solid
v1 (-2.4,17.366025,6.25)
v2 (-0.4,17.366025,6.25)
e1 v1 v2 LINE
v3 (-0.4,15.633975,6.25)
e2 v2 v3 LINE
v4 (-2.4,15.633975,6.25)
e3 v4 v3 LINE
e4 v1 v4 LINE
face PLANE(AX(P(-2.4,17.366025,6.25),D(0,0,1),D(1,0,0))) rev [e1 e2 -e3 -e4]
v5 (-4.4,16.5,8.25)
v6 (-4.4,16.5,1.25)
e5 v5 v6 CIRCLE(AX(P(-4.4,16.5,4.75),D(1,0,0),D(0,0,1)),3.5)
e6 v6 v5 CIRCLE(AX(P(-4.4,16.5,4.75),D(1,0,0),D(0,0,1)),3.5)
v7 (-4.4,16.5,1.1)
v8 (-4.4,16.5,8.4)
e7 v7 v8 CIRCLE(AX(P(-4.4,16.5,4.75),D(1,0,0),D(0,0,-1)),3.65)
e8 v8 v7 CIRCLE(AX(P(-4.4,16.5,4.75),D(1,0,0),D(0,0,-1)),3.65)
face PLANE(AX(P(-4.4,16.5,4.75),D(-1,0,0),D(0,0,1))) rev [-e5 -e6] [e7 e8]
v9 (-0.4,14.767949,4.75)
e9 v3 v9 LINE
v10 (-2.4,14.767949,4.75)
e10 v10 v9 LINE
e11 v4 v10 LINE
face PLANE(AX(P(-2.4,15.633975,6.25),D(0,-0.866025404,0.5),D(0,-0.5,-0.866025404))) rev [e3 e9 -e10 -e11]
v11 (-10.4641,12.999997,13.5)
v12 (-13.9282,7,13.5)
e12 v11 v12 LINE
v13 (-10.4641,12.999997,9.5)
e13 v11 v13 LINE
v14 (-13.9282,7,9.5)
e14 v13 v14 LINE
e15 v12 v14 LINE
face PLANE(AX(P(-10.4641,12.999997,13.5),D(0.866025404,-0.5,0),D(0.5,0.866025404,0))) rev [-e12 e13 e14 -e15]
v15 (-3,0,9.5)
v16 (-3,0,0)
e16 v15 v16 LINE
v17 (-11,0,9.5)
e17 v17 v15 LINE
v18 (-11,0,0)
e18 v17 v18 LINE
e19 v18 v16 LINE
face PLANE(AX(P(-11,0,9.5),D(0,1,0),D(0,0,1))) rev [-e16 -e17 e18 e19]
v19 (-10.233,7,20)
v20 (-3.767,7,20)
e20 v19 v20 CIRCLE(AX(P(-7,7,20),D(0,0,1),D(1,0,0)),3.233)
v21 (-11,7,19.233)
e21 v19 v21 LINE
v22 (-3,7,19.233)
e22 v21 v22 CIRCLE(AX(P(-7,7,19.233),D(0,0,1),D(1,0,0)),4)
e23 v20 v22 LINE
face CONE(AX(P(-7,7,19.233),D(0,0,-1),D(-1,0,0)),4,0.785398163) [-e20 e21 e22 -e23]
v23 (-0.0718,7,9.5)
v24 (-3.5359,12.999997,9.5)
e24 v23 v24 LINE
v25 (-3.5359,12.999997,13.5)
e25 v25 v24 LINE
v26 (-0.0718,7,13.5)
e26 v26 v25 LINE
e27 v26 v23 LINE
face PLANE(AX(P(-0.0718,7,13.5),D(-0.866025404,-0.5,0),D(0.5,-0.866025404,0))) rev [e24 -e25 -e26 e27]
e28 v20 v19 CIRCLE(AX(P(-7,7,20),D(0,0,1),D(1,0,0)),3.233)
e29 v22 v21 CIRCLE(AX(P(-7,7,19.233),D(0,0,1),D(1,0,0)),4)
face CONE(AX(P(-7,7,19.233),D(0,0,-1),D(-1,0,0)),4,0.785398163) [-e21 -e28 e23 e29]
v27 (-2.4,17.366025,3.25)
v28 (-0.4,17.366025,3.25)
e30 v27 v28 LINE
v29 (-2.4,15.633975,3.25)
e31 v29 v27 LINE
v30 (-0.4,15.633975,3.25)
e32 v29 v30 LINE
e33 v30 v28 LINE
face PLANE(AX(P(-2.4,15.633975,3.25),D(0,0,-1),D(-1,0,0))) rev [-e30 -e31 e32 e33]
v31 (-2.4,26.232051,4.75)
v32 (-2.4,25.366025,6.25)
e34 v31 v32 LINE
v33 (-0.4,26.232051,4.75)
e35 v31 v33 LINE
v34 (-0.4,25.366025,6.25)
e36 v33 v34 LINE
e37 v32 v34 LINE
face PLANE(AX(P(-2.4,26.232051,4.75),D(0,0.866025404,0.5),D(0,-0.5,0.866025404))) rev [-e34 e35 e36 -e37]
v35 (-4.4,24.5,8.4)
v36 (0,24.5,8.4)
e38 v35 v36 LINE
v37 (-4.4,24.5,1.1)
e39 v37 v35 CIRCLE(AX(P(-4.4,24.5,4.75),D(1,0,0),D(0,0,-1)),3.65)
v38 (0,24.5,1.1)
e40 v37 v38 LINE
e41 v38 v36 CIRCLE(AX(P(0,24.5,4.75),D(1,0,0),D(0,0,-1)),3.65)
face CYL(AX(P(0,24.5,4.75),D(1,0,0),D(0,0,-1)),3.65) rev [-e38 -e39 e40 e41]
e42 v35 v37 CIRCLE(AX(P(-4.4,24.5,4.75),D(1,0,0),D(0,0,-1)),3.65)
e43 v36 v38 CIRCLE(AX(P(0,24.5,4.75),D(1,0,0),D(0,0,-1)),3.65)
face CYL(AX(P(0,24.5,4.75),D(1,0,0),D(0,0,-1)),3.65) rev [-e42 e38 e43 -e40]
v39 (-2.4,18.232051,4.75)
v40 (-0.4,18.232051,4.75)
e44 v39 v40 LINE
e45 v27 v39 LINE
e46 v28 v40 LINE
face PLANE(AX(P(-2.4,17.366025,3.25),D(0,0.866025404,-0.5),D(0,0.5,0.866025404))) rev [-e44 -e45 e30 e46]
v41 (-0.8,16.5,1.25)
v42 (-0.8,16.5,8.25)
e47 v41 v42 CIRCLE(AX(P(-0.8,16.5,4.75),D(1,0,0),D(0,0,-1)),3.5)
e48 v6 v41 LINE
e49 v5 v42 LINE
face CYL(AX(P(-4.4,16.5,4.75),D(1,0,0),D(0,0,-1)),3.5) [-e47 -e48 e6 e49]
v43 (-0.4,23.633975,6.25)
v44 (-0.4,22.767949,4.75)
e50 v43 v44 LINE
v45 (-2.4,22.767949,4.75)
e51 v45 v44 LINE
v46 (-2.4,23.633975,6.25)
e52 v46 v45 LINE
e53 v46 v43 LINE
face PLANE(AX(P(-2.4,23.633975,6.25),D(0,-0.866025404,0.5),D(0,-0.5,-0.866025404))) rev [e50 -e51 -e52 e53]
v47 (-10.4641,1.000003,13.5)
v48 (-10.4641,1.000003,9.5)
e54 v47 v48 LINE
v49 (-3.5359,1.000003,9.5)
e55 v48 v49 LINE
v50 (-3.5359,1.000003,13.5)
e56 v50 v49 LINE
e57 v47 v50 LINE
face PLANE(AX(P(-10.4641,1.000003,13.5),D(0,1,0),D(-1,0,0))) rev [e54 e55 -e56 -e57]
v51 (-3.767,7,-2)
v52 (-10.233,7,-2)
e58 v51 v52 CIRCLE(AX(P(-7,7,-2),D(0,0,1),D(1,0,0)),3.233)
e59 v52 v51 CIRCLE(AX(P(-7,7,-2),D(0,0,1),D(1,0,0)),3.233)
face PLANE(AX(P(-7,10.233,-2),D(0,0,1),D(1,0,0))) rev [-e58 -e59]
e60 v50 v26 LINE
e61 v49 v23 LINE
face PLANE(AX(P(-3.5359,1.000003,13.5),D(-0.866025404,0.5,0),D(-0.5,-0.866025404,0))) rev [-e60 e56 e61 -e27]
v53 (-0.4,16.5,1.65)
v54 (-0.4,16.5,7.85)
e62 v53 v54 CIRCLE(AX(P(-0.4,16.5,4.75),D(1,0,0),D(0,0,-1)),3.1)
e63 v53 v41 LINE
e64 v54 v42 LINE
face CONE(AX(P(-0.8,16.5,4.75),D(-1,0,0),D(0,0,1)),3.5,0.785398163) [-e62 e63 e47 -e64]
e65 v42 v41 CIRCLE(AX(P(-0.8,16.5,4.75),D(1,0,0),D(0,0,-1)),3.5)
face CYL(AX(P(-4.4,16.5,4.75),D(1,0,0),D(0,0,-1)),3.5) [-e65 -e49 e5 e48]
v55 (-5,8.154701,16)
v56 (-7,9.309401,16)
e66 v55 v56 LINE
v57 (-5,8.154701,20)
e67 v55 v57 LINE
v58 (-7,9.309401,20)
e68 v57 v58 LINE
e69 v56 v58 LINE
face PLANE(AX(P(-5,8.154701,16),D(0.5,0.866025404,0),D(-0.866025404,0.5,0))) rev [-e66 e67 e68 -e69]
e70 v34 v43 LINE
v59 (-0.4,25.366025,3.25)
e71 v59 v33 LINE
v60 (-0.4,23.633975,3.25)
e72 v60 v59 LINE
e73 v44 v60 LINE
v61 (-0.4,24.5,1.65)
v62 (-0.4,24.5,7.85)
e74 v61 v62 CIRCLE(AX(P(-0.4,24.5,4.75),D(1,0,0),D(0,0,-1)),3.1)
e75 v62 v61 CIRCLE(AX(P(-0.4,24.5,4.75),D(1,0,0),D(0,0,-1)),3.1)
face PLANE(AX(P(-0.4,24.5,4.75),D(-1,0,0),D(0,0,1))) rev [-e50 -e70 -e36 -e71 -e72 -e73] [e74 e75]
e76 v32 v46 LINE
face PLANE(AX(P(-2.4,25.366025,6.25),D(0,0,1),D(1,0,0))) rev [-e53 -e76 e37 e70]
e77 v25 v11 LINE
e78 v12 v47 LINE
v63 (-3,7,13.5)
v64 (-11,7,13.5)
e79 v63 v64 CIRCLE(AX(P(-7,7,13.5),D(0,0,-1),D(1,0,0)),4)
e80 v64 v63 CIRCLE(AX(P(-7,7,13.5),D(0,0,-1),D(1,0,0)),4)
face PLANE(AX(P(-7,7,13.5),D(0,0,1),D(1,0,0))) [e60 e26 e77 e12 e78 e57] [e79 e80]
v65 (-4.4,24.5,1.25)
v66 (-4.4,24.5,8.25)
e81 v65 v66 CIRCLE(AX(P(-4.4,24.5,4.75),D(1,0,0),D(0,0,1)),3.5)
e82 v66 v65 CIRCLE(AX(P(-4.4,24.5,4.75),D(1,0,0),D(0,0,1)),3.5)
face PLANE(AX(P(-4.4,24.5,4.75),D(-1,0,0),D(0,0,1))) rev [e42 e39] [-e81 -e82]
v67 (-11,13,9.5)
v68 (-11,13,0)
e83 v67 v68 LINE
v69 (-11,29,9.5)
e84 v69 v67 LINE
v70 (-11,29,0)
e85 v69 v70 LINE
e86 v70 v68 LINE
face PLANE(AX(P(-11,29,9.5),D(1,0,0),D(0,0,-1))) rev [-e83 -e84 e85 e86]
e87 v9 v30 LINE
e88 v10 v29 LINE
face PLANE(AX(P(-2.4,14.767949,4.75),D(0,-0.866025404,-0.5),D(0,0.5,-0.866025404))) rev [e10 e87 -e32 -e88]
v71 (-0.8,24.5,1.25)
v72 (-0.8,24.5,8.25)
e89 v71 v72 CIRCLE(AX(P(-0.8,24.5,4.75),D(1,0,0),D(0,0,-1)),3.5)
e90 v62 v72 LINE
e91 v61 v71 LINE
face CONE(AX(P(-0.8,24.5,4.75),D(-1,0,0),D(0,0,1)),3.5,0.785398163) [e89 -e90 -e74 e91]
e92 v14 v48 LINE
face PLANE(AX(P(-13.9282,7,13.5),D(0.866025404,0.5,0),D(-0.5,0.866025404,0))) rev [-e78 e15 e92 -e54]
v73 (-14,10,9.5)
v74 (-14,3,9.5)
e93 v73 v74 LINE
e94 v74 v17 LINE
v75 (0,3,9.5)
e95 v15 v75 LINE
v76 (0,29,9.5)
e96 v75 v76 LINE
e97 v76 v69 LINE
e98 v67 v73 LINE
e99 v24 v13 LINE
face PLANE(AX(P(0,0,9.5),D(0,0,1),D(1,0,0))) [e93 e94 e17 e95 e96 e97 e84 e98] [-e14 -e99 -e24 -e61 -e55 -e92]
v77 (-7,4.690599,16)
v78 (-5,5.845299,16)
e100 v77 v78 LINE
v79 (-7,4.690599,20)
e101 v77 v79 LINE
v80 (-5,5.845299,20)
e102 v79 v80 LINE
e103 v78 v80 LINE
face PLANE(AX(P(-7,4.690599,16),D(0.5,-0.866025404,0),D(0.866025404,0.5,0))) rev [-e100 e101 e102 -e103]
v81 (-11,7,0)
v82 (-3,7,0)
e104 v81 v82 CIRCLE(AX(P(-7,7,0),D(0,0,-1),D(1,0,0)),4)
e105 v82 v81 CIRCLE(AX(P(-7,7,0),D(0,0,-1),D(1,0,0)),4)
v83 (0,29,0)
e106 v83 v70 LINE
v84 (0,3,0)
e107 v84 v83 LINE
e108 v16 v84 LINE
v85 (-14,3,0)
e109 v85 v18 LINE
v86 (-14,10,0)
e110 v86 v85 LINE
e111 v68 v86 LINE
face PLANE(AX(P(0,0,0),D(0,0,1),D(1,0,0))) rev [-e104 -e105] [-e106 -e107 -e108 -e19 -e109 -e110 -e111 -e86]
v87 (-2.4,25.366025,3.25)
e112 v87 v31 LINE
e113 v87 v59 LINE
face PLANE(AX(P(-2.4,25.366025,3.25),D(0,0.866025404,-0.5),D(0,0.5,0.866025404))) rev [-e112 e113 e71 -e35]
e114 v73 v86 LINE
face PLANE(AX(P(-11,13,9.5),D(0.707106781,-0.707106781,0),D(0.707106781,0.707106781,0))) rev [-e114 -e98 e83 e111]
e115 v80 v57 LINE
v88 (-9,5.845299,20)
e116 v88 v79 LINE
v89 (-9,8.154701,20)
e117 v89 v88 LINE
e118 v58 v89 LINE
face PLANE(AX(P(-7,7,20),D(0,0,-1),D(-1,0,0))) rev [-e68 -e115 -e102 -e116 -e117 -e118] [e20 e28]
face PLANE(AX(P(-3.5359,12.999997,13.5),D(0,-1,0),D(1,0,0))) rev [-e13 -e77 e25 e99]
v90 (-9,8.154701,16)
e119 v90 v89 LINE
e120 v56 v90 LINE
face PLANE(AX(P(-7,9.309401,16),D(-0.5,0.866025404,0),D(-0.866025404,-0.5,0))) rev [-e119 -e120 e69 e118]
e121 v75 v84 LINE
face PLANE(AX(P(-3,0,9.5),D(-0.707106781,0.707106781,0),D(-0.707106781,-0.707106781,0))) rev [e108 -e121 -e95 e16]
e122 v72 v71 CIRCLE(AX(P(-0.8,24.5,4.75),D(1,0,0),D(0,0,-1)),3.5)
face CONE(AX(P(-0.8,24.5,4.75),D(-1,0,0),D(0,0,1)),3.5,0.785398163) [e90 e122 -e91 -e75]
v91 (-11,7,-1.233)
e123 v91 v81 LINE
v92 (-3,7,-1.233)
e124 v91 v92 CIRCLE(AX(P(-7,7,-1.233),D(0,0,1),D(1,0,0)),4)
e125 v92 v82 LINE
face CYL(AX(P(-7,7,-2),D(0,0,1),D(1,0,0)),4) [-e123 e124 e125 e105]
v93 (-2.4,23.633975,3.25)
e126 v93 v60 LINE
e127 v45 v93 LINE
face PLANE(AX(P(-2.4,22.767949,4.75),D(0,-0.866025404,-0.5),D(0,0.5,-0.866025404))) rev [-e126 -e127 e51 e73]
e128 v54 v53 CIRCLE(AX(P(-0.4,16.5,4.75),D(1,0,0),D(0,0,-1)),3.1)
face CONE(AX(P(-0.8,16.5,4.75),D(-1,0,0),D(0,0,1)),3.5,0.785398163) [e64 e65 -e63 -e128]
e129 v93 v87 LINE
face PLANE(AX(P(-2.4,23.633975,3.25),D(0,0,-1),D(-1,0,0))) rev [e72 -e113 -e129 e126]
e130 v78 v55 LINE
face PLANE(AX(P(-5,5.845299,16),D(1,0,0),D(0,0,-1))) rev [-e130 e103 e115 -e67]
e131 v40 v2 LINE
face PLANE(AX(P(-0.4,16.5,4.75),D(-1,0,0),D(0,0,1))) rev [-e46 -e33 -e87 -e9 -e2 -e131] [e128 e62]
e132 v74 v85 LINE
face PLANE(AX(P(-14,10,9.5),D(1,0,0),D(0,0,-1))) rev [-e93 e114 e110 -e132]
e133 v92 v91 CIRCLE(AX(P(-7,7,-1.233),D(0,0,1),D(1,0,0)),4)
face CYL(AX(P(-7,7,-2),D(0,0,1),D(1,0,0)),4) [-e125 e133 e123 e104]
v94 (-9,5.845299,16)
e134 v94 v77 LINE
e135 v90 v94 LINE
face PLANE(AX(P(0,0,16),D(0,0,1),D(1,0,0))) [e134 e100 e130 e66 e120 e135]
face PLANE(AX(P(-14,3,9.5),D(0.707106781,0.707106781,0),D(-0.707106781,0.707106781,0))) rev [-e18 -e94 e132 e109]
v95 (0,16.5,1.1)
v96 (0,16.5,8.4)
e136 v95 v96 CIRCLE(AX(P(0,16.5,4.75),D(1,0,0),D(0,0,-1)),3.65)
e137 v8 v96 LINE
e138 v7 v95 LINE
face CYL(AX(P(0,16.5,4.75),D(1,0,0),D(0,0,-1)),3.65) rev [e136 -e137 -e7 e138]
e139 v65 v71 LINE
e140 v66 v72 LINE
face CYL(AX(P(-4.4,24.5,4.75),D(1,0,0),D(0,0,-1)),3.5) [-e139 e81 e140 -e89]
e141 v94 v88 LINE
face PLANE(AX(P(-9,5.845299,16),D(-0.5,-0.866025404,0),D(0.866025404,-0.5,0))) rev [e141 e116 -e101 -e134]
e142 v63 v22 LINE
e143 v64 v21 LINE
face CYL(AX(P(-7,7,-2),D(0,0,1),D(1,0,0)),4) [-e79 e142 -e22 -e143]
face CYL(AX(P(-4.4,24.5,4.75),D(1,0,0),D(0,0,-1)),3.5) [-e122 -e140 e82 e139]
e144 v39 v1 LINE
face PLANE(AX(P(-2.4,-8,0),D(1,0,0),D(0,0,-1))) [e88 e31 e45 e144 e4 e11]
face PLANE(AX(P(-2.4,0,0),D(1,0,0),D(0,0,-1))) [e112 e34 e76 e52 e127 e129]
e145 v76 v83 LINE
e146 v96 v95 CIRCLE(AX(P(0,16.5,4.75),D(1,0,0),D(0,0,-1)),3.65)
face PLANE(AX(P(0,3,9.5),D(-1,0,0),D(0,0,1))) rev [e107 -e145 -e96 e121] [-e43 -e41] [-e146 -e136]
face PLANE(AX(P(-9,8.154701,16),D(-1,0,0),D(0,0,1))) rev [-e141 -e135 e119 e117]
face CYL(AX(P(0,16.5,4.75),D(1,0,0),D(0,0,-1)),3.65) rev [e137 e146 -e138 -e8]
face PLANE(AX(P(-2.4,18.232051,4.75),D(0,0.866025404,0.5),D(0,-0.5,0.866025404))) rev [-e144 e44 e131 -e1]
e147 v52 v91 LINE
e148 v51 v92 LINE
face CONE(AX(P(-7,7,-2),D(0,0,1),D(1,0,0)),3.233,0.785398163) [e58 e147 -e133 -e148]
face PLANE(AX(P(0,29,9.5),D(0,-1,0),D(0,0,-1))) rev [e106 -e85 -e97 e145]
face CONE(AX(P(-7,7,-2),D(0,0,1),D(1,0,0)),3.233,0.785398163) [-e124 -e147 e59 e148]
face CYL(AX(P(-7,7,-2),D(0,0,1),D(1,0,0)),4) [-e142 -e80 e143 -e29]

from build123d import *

# Parameters (mm, degrees)
EXTRUDE_1_DEPTH        = 9.5
SKETCH_3_R             = 11
EXTRUDE_2_DEPTH        = 4
SKETCH_4_R             = 11
CUT_EXTRUDE_1_DEPTH    = 4
CUT_EXTRUDE_2_DEPTH    = 4
HOLE_WIZARD_1_D        = 7.3
HOLE_WIZARD_1_DEPTH    = 4.4
PATTERN_LINEAR_1_COUNT = 2
PATTERN_LINEAR_1_PITCH = 8
CUT_EXTRUDE_3_DEPTH    = 2
PATTERN_LINEAR_2_COUNT = 2
PATTERN_LINEAR_2_PITCH = 8


with BuildPart() as part:
    # 草图1 → 凸台-拉伸1 (new body)
    with BuildSketch(Plane.XY):
        Polygon((-14, 3), (-11, 0), (-3, 0), (0, 3), (0, 29), (-11, 29), (-11, 13), (-14, 10), align=None)
    extrude(amount=EXTRUDE_1_DEPTH)

    # 草图3 → 凸台-拉伸2 (add)
    with BuildSketch(Plane.XY.offset(9.5)):
        with Locations(Location((-7, 7, 0), (0, 0, 111.323686263))):
            Circle(SKETCH_3_R)
    extrude(amount=EXTRUDE_2_DEPTH)

    # 草图4 → 切除-拉伸1 (cut)
    with BuildSketch(Plane.XY.offset(9.5)):
        with Locations((-7, 7)):
            Circle(SKETCH_4_R)
        Polygon((-13.9282, 7), (-10.4641, 1.000002798), (-3.5359, 1.000002798), (-0.0718, 7), (-3.5359, 12.999997202), (-10.4641, 12.999997202), align=None, mode=Mode.SUBTRACT)
    extrude(amount=CUT_EXTRUDE_1_DEPTH, mode=Mode.SUBTRACT)

    # 草图2 → 旋转1 (revolve)
    with BuildSketch(Plane(origin=(-7, 0, 0), x_dir=(0, 0, -1), z_dir=(1, 0, 0)), mode=Mode.PRIVATE) as revolve_1_sk:
        Polygon((-20, 7), (-20, 10.233), (-19.233, 11), (1.233, 11), (2, 10.233), (2, 7), align=None)
    revolve(revolve_1_sk.sketch.rotate(Axis((-7, 7, -2), (0, 0, 1)), 270), axis=Axis((-7, 7, -2), (0, 0, 1)))

    # 草图5 → 切除-拉伸2 (cut)
    with BuildSketch(Plane.XY.offset(20)):
        Polygon((-9, 8.154700538), (-9, 5.845299462), (-7, 4.690598923), (-5, 5.845299462), (-5, 8.154700538), (-7, 9.309401077), align=None)
    extrude(amount=-CUT_EXTRUDE_2_DEPTH, mode=Mode.SUBTRACT)

    # 孔1
    with Locations(Plane(origin=(0, 0, 0), x_dir=(0, 0, -1), z_dir=(1, 0, 0))):
        with Locations((-4.75, 24.5)):
            hole_wizard_1 = Hole(HOLE_WIZARD_1_D / 2, depth=HOLE_WIZARD_1_DEPTH)

    # 阵列(线性)1: 孔1 ×2
    with Locations(*[(0, -i * PATTERN_LINEAR_1_PITCH, 0) for i in range(1, PATTERN_LINEAR_1_COUNT)]):
        add(hole_wizard_1, mode=Mode.SUBTRACT)

    # 草图9 → 旋转2 (revolve)
    with BuildSketch(Plane(origin=(0, 24.5, 0), x_dir=(1, 0, 0), z_dir=(0, 1, 0)), mode=Mode.PRIVATE) as revolve_2_sk:
        Polygon((-0.4, -4.75), (-0.4, -7.85), (-0.8, -8.25), (-4.4, -8.25), (-4.4, -4.75), align=None)
    revolve(revolve_2_sk.sketch.rotate(Axis((-4.4, 24.5, 4.75), (1, 0, 0)), 180), axis=Axis((-4.4, 24.5, 4.75), (1, 0, 0)))

    # 草图10 → 旋转3 (revolve)
    with BuildSketch(Plane(origin=(0, 16.5, 0), x_dir=(1, 0, 0), z_dir=(0, 1, 0)), mode=Mode.PRIVATE) as revolve_3_sk:
        Polygon((-0.4, -4.75), (-0.4, -7.85), (-0.8, -8.25), (-4.4, -8.25), (-4.4, -4.75), align=None)
    revolve(revolve_3_sk.sketch.rotate(Axis((-4.4, 16.5, 4.75), (1, 0, 0)), 180), axis=Axis((-4.4, 16.5, 4.75), (1, 0, 0)))

    # 草图11 → 切除-拉伸3 (cut)
    with BuildSketch(Plane(origin=(-0.4, 0, 0), x_dir=(0, 0, -1), z_dir=(1, 0, 0))):
        Polygon((-6.25, 25.366025404), (-6.25, 23.633974596), (-4.75, 22.767949192), (-3.25, 23.633974596), (-3.25, 25.366025404), (-4.75, 26.232050808), align=None)
    cut_extrude_3 = extrude(amount=-CUT_EXTRUDE_3_DEPTH, mode=Mode.SUBTRACT)

    # 阵列(线性)2: 切除-拉伸3 ×2
    with Locations(*[(0, -i * PATTERN_LINEAR_2_PITCH, 0) for i in range(1, PATTERN_LINEAR_2_COUNT)]):
        add(cut_extrude_3, mode=Mode.SUBTRACT)


solid = part.part
